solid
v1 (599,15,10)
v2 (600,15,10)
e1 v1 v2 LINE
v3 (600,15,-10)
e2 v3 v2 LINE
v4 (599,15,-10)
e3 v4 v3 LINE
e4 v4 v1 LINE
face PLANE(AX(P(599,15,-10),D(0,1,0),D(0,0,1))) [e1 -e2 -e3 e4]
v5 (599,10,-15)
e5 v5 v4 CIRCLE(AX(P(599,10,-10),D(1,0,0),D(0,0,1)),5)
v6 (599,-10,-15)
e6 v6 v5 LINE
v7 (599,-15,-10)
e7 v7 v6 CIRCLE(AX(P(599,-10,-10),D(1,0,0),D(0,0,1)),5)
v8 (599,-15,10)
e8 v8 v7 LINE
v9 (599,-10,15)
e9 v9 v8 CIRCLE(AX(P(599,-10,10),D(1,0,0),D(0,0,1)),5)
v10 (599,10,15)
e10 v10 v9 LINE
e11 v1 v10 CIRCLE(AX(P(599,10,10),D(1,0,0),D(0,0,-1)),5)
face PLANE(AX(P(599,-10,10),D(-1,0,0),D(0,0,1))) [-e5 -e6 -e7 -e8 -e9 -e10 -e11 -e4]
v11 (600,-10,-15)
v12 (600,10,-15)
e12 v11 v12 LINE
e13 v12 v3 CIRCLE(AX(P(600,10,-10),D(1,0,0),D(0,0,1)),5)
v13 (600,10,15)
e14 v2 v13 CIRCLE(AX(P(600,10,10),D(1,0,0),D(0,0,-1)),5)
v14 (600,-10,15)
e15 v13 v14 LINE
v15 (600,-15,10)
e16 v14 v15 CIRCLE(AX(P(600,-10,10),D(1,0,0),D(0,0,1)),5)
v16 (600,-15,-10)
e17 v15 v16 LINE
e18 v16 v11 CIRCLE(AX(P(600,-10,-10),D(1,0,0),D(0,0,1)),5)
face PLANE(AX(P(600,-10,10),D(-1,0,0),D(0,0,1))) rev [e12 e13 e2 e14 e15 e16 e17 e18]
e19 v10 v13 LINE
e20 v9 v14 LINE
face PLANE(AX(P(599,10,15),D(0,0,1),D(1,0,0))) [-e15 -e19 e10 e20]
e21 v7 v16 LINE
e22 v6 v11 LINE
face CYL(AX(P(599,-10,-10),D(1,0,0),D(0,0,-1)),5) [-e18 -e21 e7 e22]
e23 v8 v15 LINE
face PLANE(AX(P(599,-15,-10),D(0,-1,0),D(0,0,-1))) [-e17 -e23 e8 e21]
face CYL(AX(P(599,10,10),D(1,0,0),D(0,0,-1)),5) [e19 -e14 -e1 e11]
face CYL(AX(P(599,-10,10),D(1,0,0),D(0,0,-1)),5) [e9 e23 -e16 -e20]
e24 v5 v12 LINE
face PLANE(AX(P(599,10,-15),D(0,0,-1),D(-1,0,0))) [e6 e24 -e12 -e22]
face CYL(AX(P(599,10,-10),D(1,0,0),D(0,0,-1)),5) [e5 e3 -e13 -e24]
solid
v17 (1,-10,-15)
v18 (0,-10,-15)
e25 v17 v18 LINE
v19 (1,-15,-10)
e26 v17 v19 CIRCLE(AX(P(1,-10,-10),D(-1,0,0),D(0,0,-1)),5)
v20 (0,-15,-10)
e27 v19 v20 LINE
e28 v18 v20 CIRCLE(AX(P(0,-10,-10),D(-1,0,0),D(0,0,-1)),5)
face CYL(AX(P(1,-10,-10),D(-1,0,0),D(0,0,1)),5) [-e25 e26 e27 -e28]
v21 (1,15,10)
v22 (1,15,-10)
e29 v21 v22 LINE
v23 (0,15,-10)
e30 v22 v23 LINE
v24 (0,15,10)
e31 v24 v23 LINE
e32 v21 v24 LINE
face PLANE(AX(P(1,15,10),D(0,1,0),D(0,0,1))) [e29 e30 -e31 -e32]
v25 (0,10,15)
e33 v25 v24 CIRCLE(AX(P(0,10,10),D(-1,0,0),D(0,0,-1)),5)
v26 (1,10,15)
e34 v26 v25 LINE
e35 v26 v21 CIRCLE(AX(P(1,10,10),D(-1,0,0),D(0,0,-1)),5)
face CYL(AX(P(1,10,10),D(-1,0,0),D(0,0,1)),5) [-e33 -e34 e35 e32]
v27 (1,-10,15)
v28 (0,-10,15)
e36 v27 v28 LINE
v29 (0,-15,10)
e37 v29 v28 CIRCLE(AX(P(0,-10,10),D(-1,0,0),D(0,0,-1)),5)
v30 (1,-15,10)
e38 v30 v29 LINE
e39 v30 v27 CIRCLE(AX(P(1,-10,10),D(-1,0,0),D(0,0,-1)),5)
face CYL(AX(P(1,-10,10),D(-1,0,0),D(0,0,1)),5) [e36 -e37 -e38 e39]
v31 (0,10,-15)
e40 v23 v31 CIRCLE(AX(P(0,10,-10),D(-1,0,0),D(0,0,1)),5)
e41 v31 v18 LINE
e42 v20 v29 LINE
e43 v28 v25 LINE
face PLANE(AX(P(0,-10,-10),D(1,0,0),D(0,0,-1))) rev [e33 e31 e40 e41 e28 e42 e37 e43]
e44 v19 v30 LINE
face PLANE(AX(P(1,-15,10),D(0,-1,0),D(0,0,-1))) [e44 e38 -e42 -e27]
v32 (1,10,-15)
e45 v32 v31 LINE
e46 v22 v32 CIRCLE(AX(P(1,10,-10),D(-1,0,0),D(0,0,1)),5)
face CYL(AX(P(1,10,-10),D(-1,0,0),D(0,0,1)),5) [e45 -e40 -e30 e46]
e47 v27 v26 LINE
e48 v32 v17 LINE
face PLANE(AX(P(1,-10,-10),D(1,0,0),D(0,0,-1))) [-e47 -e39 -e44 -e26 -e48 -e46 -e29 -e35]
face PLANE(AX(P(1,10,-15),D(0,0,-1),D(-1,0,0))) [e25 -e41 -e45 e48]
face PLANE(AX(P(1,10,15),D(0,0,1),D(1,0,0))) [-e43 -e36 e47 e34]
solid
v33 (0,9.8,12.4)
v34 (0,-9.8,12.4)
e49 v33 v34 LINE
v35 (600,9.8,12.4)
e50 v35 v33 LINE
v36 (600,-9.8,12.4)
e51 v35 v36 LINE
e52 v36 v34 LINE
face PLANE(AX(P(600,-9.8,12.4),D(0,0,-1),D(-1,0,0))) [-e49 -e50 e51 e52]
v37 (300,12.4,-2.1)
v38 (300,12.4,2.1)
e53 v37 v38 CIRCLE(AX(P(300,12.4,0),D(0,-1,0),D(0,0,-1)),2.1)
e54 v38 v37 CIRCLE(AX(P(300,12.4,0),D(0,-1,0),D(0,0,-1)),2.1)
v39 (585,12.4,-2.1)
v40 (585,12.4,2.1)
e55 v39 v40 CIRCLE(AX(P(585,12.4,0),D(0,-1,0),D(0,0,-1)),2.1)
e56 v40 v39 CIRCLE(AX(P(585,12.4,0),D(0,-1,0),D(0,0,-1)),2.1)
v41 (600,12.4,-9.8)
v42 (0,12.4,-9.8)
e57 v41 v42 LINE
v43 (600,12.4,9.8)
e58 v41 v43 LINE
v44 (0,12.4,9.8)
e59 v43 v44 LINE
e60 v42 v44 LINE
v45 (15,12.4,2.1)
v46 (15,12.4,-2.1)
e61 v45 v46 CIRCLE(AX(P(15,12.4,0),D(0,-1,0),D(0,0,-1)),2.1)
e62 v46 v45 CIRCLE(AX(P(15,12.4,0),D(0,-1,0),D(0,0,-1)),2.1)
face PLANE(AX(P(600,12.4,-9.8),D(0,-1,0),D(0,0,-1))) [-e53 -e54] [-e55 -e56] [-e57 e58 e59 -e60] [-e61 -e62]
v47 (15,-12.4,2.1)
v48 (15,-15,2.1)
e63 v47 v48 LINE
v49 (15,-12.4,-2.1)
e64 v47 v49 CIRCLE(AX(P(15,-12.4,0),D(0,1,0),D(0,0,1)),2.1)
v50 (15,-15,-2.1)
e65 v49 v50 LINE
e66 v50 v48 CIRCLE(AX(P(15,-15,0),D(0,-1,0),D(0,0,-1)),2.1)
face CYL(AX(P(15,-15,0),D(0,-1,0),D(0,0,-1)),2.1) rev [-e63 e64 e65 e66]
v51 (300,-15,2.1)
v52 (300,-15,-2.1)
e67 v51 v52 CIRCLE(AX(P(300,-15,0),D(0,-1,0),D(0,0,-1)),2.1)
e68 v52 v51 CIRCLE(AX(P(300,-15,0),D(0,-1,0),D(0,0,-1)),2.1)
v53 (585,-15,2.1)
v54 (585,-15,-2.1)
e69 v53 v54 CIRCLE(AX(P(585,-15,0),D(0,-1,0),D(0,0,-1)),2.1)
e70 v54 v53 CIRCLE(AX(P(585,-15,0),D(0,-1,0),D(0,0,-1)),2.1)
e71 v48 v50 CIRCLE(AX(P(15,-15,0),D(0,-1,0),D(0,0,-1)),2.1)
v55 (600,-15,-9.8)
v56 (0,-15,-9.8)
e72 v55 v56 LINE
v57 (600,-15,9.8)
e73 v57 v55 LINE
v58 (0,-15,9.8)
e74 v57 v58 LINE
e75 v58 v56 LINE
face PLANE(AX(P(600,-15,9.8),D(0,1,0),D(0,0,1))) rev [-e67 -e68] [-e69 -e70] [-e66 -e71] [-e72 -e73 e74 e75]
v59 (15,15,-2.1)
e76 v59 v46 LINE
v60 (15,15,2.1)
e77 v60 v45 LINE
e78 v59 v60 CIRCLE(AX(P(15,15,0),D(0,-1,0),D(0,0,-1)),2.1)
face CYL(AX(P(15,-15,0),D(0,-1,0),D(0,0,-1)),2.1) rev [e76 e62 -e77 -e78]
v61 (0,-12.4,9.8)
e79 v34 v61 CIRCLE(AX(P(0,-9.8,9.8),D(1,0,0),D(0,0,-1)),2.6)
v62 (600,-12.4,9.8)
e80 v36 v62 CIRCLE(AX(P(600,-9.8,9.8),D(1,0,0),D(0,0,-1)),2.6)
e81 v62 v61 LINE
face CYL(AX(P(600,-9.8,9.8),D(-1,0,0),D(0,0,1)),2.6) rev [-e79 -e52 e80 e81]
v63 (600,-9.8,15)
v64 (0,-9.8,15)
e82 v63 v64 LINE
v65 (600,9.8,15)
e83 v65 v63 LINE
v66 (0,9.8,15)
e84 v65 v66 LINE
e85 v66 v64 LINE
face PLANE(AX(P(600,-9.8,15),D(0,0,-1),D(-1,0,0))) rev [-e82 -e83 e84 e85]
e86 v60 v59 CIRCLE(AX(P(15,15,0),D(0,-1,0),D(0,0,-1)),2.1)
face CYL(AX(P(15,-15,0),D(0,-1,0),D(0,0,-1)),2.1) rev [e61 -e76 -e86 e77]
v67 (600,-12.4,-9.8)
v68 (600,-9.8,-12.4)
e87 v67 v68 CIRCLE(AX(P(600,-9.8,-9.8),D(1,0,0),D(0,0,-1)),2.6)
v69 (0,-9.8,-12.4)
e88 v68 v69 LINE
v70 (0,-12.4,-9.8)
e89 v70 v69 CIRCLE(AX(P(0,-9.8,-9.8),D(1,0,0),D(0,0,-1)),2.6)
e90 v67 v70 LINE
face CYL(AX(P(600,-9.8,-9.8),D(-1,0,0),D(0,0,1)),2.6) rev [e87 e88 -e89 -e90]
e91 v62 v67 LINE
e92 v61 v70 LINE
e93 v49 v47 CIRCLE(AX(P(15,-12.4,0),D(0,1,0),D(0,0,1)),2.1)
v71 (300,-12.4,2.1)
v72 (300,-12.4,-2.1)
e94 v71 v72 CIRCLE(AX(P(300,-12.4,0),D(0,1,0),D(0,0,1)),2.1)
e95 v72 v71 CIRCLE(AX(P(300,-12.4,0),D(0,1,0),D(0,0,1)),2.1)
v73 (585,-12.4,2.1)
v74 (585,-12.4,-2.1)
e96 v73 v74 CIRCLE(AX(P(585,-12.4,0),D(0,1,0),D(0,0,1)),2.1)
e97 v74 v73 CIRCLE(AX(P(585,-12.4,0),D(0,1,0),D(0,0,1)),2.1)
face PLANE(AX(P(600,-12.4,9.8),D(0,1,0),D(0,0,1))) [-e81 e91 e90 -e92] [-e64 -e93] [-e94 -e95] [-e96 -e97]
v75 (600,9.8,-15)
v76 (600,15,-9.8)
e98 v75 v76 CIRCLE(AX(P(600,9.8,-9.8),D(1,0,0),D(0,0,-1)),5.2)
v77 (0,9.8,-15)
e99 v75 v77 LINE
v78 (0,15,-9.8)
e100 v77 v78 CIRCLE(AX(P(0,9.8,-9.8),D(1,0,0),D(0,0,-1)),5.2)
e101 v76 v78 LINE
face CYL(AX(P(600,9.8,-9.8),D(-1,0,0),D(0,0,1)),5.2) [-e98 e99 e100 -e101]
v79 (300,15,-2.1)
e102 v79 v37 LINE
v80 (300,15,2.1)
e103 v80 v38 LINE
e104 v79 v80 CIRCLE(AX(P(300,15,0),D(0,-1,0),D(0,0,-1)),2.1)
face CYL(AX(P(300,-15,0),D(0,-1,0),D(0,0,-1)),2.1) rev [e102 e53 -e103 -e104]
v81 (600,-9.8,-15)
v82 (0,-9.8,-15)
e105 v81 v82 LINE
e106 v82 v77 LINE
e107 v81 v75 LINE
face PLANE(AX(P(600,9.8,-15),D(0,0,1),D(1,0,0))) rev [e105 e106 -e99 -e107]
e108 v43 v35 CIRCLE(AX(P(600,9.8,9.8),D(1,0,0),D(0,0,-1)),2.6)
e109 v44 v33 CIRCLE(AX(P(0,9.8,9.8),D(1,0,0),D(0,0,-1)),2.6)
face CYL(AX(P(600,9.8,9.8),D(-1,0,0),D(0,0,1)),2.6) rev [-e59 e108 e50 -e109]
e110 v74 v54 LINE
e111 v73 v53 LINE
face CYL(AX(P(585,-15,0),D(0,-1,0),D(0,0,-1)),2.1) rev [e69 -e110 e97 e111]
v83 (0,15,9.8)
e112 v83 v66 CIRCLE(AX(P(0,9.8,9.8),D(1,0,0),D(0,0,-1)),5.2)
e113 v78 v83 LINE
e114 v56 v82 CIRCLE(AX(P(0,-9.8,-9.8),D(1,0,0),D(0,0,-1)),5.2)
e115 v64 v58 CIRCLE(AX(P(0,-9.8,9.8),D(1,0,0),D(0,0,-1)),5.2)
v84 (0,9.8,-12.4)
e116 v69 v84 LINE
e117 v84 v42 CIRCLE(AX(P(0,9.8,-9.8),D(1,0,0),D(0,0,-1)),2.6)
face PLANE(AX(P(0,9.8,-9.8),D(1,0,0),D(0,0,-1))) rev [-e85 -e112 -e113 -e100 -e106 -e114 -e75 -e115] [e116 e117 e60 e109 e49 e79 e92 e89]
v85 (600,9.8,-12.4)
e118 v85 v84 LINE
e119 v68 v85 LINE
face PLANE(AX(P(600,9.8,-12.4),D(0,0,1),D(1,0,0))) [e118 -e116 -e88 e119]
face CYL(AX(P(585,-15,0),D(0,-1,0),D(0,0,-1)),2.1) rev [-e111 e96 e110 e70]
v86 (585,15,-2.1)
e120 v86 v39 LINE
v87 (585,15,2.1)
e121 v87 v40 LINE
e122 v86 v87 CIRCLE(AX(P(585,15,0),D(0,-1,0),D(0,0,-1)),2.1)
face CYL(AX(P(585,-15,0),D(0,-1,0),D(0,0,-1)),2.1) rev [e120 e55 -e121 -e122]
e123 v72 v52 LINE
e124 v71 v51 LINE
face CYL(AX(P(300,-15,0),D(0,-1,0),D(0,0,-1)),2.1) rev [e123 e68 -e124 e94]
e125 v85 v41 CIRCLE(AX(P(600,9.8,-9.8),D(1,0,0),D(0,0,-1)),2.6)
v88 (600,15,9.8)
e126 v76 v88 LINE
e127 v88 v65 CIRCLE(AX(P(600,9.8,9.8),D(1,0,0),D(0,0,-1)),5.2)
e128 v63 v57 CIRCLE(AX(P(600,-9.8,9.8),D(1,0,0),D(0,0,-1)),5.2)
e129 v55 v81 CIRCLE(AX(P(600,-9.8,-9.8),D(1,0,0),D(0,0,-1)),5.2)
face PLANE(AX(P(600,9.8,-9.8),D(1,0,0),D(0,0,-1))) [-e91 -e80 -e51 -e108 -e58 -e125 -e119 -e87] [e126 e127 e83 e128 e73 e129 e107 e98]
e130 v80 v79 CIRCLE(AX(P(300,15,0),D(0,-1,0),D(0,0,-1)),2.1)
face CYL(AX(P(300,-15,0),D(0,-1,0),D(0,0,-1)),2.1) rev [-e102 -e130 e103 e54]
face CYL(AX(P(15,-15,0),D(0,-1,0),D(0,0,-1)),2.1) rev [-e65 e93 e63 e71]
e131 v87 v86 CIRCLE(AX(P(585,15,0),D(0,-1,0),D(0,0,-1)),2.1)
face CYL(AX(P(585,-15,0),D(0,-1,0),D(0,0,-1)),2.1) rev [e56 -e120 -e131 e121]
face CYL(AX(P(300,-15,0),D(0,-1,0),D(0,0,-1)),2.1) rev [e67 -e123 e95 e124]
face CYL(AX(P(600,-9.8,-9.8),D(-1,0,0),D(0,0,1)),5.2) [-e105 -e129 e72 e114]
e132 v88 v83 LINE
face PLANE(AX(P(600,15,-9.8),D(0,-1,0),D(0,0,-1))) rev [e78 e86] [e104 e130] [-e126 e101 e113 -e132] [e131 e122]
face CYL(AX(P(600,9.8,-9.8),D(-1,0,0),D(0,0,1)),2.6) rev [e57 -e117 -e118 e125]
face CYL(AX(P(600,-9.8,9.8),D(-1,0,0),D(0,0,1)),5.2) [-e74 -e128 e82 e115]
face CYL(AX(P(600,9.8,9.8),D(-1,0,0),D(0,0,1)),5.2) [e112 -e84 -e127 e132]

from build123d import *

# Parameters (mm, degrees)
MEMBER_1_DEPTH              = 600
EXTRUDE_1_DEPTH             = 1
EXTRUDE_2_DEPTH             = 1
SKETCH_5_W                  = 2.1
SKETCH_5_H                  = 30
HOLE_WIZARD_M5_1_AT_2_COUNT = 2
HOLE_WIZARD_M5_1_AT_2_PITCH = 285
HOLE_WIZARD_M5_1_AT_3_COUNT = 2
HOLE_WIZARD_M5_1_AT_3_PITCH = 570


with BuildPart() as part:
    # Sketch1 → Member 1 (new body)
    with BuildSketch(Plane(origin=(0, 0, 0), x_dir=(0, 0, -1), z_dir=(1, 0, 0))):
        with BuildLine():
            Line((-9.8, -15), (9.8, -15))
            ThreePointArc((9.8, -15), (13.476955262, -13.476955262), (15, -9.8))
            Line((15, -9.8), (15, 9.8))
            ThreePointArc((15, 9.8), (13.476955262, 13.476955262), (9.8, 15))
            Line((9.8, 15), (-9.8, 15))
            ThreePointArc((-9.8, 15), (-13.476955262, 13.476955262), (-15, 9.8))
            Line((-15, 9.8), (-15, -9.8))
            ThreePointArc((-15, -9.8), (-13.476955262, -13.476955262), (-9.8, -15))
        make_face()
        with BuildLine():
            Line((-9.8, -12.4), (9.8, -12.4))
            ThreePointArc((9.8, -12.4), (11.638477631, -11.638477631), (12.4, -9.8))
            Line((12.4, -9.8), (12.4, 9.8))
            ThreePointArc((12.4, 9.8), (11.638477631, 11.638477631), (9.8, 12.4))
            Line((9.8, 12.4), (-9.8, 12.4))
            ThreePointArc((-9.8, 12.4), (-11.638477631, 11.638477631), (-12.4, 9.8))
            Line((-12.4, 9.8), (-12.4, -9.8))
            ThreePointArc((-12.4, -9.8), (-11.638477631, -11.638477631), (-9.8, -12.4))
        make_face(mode=Mode.SUBTRACT)
    extrude(amount=MEMBER_1_DEPTH)

    # 草图5 → M5 螺纹孔1 (revolve, cut)
    with BuildSketch(Plane(origin=(14.999999998, -15, 1e-09), x_dir=(0, 0, -1), z_dir=(1, 0, 0))):
        with Locations((1.05, 15)):
            Rectangle(SKETCH_5_W, SKETCH_5_H)
    hole_wizard_m5_1 = revolve(axis=Axis((14.999999998, -21.35, 1e-09), (0, 1, 0)), mode=Mode.SUBTRACT)

    # M5 螺纹孔1 at 2: M5 螺纹孔1 ×2
    with Locations(*[(i * HOLE_WIZARD_M5_1_AT_2_PITCH, 0, 0) for i in range(1, HOLE_WIZARD_M5_1_AT_2_COUNT)]):
        add(hole_wizard_m5_1, mode=Mode.SUBTRACT)

    # M5 螺纹孔1 at 3: M5 螺纹孔1 ×2
    with Locations(*[(i * HOLE_WIZARD_M5_1_AT_3_PITCH, 0, 0) for i in range(1, HOLE_WIZARD_M5_1_AT_3_COUNT)]):
        add(hole_wizard_m5_1, mode=Mode.SUBTRACT)


with BuildPart() as body_2:
    # 草图1 → 凸台-拉伸1 (new body)
    with BuildSketch(Plane.ZY):
        with BuildLine():
            Line((10, 15), (-10, 15))
            ThreePointArc((-10, 15), (-13.535533906, 13.535533906), (-15, 10))
            Line((-15, 10), (-15, -10))
            ThreePointArc((-15, -10), (-13.535533906, -13.535533906), (-10, -15))
            Line((-10, -15), (10, -15))
            ThreePointArc((10, -15), (13.535533906, -13.535533906), (15, -10))
            Line((15, -10), (15, 10))
            ThreePointArc((15, 10), (13.535533906, 13.535533906), (10, 15))
        make_face()
    extrude(amount=-EXTRUDE_1_DEPTH)


with BuildPart() as body_3:
    # 草图2 → 凸台-拉伸2 (new body)
    with BuildSketch(Plane(origin=(600, 0, 0), x_dir=(0, 0, -1), z_dir=(1, 0, 0))):
        with BuildLine():
            Line((10, 15), (-10, 15))
            ThreePointArc((-10, 15), (-13.535533906, 13.535533906), (-15, 10))
            Line((-15, 10), (-15, -10))
            ThreePointArc((-15, -10), (-13.535533906, -13.535533906), (-10, -15))
            Line((-10, -15), (10, -15))
            ThreePointArc((10, -15), (13.535533906, -13.535533906), (15, -10))
            Line((15, -10), (15, 10))
            ThreePointArc((15, 10), (13.535533906, 13.535533906), (10, 15))
        make_face()
    extrude(amount=-EXTRUDE_2_DEPTH)


solid = Compound([part.part, body_2.part, body_3.part])
